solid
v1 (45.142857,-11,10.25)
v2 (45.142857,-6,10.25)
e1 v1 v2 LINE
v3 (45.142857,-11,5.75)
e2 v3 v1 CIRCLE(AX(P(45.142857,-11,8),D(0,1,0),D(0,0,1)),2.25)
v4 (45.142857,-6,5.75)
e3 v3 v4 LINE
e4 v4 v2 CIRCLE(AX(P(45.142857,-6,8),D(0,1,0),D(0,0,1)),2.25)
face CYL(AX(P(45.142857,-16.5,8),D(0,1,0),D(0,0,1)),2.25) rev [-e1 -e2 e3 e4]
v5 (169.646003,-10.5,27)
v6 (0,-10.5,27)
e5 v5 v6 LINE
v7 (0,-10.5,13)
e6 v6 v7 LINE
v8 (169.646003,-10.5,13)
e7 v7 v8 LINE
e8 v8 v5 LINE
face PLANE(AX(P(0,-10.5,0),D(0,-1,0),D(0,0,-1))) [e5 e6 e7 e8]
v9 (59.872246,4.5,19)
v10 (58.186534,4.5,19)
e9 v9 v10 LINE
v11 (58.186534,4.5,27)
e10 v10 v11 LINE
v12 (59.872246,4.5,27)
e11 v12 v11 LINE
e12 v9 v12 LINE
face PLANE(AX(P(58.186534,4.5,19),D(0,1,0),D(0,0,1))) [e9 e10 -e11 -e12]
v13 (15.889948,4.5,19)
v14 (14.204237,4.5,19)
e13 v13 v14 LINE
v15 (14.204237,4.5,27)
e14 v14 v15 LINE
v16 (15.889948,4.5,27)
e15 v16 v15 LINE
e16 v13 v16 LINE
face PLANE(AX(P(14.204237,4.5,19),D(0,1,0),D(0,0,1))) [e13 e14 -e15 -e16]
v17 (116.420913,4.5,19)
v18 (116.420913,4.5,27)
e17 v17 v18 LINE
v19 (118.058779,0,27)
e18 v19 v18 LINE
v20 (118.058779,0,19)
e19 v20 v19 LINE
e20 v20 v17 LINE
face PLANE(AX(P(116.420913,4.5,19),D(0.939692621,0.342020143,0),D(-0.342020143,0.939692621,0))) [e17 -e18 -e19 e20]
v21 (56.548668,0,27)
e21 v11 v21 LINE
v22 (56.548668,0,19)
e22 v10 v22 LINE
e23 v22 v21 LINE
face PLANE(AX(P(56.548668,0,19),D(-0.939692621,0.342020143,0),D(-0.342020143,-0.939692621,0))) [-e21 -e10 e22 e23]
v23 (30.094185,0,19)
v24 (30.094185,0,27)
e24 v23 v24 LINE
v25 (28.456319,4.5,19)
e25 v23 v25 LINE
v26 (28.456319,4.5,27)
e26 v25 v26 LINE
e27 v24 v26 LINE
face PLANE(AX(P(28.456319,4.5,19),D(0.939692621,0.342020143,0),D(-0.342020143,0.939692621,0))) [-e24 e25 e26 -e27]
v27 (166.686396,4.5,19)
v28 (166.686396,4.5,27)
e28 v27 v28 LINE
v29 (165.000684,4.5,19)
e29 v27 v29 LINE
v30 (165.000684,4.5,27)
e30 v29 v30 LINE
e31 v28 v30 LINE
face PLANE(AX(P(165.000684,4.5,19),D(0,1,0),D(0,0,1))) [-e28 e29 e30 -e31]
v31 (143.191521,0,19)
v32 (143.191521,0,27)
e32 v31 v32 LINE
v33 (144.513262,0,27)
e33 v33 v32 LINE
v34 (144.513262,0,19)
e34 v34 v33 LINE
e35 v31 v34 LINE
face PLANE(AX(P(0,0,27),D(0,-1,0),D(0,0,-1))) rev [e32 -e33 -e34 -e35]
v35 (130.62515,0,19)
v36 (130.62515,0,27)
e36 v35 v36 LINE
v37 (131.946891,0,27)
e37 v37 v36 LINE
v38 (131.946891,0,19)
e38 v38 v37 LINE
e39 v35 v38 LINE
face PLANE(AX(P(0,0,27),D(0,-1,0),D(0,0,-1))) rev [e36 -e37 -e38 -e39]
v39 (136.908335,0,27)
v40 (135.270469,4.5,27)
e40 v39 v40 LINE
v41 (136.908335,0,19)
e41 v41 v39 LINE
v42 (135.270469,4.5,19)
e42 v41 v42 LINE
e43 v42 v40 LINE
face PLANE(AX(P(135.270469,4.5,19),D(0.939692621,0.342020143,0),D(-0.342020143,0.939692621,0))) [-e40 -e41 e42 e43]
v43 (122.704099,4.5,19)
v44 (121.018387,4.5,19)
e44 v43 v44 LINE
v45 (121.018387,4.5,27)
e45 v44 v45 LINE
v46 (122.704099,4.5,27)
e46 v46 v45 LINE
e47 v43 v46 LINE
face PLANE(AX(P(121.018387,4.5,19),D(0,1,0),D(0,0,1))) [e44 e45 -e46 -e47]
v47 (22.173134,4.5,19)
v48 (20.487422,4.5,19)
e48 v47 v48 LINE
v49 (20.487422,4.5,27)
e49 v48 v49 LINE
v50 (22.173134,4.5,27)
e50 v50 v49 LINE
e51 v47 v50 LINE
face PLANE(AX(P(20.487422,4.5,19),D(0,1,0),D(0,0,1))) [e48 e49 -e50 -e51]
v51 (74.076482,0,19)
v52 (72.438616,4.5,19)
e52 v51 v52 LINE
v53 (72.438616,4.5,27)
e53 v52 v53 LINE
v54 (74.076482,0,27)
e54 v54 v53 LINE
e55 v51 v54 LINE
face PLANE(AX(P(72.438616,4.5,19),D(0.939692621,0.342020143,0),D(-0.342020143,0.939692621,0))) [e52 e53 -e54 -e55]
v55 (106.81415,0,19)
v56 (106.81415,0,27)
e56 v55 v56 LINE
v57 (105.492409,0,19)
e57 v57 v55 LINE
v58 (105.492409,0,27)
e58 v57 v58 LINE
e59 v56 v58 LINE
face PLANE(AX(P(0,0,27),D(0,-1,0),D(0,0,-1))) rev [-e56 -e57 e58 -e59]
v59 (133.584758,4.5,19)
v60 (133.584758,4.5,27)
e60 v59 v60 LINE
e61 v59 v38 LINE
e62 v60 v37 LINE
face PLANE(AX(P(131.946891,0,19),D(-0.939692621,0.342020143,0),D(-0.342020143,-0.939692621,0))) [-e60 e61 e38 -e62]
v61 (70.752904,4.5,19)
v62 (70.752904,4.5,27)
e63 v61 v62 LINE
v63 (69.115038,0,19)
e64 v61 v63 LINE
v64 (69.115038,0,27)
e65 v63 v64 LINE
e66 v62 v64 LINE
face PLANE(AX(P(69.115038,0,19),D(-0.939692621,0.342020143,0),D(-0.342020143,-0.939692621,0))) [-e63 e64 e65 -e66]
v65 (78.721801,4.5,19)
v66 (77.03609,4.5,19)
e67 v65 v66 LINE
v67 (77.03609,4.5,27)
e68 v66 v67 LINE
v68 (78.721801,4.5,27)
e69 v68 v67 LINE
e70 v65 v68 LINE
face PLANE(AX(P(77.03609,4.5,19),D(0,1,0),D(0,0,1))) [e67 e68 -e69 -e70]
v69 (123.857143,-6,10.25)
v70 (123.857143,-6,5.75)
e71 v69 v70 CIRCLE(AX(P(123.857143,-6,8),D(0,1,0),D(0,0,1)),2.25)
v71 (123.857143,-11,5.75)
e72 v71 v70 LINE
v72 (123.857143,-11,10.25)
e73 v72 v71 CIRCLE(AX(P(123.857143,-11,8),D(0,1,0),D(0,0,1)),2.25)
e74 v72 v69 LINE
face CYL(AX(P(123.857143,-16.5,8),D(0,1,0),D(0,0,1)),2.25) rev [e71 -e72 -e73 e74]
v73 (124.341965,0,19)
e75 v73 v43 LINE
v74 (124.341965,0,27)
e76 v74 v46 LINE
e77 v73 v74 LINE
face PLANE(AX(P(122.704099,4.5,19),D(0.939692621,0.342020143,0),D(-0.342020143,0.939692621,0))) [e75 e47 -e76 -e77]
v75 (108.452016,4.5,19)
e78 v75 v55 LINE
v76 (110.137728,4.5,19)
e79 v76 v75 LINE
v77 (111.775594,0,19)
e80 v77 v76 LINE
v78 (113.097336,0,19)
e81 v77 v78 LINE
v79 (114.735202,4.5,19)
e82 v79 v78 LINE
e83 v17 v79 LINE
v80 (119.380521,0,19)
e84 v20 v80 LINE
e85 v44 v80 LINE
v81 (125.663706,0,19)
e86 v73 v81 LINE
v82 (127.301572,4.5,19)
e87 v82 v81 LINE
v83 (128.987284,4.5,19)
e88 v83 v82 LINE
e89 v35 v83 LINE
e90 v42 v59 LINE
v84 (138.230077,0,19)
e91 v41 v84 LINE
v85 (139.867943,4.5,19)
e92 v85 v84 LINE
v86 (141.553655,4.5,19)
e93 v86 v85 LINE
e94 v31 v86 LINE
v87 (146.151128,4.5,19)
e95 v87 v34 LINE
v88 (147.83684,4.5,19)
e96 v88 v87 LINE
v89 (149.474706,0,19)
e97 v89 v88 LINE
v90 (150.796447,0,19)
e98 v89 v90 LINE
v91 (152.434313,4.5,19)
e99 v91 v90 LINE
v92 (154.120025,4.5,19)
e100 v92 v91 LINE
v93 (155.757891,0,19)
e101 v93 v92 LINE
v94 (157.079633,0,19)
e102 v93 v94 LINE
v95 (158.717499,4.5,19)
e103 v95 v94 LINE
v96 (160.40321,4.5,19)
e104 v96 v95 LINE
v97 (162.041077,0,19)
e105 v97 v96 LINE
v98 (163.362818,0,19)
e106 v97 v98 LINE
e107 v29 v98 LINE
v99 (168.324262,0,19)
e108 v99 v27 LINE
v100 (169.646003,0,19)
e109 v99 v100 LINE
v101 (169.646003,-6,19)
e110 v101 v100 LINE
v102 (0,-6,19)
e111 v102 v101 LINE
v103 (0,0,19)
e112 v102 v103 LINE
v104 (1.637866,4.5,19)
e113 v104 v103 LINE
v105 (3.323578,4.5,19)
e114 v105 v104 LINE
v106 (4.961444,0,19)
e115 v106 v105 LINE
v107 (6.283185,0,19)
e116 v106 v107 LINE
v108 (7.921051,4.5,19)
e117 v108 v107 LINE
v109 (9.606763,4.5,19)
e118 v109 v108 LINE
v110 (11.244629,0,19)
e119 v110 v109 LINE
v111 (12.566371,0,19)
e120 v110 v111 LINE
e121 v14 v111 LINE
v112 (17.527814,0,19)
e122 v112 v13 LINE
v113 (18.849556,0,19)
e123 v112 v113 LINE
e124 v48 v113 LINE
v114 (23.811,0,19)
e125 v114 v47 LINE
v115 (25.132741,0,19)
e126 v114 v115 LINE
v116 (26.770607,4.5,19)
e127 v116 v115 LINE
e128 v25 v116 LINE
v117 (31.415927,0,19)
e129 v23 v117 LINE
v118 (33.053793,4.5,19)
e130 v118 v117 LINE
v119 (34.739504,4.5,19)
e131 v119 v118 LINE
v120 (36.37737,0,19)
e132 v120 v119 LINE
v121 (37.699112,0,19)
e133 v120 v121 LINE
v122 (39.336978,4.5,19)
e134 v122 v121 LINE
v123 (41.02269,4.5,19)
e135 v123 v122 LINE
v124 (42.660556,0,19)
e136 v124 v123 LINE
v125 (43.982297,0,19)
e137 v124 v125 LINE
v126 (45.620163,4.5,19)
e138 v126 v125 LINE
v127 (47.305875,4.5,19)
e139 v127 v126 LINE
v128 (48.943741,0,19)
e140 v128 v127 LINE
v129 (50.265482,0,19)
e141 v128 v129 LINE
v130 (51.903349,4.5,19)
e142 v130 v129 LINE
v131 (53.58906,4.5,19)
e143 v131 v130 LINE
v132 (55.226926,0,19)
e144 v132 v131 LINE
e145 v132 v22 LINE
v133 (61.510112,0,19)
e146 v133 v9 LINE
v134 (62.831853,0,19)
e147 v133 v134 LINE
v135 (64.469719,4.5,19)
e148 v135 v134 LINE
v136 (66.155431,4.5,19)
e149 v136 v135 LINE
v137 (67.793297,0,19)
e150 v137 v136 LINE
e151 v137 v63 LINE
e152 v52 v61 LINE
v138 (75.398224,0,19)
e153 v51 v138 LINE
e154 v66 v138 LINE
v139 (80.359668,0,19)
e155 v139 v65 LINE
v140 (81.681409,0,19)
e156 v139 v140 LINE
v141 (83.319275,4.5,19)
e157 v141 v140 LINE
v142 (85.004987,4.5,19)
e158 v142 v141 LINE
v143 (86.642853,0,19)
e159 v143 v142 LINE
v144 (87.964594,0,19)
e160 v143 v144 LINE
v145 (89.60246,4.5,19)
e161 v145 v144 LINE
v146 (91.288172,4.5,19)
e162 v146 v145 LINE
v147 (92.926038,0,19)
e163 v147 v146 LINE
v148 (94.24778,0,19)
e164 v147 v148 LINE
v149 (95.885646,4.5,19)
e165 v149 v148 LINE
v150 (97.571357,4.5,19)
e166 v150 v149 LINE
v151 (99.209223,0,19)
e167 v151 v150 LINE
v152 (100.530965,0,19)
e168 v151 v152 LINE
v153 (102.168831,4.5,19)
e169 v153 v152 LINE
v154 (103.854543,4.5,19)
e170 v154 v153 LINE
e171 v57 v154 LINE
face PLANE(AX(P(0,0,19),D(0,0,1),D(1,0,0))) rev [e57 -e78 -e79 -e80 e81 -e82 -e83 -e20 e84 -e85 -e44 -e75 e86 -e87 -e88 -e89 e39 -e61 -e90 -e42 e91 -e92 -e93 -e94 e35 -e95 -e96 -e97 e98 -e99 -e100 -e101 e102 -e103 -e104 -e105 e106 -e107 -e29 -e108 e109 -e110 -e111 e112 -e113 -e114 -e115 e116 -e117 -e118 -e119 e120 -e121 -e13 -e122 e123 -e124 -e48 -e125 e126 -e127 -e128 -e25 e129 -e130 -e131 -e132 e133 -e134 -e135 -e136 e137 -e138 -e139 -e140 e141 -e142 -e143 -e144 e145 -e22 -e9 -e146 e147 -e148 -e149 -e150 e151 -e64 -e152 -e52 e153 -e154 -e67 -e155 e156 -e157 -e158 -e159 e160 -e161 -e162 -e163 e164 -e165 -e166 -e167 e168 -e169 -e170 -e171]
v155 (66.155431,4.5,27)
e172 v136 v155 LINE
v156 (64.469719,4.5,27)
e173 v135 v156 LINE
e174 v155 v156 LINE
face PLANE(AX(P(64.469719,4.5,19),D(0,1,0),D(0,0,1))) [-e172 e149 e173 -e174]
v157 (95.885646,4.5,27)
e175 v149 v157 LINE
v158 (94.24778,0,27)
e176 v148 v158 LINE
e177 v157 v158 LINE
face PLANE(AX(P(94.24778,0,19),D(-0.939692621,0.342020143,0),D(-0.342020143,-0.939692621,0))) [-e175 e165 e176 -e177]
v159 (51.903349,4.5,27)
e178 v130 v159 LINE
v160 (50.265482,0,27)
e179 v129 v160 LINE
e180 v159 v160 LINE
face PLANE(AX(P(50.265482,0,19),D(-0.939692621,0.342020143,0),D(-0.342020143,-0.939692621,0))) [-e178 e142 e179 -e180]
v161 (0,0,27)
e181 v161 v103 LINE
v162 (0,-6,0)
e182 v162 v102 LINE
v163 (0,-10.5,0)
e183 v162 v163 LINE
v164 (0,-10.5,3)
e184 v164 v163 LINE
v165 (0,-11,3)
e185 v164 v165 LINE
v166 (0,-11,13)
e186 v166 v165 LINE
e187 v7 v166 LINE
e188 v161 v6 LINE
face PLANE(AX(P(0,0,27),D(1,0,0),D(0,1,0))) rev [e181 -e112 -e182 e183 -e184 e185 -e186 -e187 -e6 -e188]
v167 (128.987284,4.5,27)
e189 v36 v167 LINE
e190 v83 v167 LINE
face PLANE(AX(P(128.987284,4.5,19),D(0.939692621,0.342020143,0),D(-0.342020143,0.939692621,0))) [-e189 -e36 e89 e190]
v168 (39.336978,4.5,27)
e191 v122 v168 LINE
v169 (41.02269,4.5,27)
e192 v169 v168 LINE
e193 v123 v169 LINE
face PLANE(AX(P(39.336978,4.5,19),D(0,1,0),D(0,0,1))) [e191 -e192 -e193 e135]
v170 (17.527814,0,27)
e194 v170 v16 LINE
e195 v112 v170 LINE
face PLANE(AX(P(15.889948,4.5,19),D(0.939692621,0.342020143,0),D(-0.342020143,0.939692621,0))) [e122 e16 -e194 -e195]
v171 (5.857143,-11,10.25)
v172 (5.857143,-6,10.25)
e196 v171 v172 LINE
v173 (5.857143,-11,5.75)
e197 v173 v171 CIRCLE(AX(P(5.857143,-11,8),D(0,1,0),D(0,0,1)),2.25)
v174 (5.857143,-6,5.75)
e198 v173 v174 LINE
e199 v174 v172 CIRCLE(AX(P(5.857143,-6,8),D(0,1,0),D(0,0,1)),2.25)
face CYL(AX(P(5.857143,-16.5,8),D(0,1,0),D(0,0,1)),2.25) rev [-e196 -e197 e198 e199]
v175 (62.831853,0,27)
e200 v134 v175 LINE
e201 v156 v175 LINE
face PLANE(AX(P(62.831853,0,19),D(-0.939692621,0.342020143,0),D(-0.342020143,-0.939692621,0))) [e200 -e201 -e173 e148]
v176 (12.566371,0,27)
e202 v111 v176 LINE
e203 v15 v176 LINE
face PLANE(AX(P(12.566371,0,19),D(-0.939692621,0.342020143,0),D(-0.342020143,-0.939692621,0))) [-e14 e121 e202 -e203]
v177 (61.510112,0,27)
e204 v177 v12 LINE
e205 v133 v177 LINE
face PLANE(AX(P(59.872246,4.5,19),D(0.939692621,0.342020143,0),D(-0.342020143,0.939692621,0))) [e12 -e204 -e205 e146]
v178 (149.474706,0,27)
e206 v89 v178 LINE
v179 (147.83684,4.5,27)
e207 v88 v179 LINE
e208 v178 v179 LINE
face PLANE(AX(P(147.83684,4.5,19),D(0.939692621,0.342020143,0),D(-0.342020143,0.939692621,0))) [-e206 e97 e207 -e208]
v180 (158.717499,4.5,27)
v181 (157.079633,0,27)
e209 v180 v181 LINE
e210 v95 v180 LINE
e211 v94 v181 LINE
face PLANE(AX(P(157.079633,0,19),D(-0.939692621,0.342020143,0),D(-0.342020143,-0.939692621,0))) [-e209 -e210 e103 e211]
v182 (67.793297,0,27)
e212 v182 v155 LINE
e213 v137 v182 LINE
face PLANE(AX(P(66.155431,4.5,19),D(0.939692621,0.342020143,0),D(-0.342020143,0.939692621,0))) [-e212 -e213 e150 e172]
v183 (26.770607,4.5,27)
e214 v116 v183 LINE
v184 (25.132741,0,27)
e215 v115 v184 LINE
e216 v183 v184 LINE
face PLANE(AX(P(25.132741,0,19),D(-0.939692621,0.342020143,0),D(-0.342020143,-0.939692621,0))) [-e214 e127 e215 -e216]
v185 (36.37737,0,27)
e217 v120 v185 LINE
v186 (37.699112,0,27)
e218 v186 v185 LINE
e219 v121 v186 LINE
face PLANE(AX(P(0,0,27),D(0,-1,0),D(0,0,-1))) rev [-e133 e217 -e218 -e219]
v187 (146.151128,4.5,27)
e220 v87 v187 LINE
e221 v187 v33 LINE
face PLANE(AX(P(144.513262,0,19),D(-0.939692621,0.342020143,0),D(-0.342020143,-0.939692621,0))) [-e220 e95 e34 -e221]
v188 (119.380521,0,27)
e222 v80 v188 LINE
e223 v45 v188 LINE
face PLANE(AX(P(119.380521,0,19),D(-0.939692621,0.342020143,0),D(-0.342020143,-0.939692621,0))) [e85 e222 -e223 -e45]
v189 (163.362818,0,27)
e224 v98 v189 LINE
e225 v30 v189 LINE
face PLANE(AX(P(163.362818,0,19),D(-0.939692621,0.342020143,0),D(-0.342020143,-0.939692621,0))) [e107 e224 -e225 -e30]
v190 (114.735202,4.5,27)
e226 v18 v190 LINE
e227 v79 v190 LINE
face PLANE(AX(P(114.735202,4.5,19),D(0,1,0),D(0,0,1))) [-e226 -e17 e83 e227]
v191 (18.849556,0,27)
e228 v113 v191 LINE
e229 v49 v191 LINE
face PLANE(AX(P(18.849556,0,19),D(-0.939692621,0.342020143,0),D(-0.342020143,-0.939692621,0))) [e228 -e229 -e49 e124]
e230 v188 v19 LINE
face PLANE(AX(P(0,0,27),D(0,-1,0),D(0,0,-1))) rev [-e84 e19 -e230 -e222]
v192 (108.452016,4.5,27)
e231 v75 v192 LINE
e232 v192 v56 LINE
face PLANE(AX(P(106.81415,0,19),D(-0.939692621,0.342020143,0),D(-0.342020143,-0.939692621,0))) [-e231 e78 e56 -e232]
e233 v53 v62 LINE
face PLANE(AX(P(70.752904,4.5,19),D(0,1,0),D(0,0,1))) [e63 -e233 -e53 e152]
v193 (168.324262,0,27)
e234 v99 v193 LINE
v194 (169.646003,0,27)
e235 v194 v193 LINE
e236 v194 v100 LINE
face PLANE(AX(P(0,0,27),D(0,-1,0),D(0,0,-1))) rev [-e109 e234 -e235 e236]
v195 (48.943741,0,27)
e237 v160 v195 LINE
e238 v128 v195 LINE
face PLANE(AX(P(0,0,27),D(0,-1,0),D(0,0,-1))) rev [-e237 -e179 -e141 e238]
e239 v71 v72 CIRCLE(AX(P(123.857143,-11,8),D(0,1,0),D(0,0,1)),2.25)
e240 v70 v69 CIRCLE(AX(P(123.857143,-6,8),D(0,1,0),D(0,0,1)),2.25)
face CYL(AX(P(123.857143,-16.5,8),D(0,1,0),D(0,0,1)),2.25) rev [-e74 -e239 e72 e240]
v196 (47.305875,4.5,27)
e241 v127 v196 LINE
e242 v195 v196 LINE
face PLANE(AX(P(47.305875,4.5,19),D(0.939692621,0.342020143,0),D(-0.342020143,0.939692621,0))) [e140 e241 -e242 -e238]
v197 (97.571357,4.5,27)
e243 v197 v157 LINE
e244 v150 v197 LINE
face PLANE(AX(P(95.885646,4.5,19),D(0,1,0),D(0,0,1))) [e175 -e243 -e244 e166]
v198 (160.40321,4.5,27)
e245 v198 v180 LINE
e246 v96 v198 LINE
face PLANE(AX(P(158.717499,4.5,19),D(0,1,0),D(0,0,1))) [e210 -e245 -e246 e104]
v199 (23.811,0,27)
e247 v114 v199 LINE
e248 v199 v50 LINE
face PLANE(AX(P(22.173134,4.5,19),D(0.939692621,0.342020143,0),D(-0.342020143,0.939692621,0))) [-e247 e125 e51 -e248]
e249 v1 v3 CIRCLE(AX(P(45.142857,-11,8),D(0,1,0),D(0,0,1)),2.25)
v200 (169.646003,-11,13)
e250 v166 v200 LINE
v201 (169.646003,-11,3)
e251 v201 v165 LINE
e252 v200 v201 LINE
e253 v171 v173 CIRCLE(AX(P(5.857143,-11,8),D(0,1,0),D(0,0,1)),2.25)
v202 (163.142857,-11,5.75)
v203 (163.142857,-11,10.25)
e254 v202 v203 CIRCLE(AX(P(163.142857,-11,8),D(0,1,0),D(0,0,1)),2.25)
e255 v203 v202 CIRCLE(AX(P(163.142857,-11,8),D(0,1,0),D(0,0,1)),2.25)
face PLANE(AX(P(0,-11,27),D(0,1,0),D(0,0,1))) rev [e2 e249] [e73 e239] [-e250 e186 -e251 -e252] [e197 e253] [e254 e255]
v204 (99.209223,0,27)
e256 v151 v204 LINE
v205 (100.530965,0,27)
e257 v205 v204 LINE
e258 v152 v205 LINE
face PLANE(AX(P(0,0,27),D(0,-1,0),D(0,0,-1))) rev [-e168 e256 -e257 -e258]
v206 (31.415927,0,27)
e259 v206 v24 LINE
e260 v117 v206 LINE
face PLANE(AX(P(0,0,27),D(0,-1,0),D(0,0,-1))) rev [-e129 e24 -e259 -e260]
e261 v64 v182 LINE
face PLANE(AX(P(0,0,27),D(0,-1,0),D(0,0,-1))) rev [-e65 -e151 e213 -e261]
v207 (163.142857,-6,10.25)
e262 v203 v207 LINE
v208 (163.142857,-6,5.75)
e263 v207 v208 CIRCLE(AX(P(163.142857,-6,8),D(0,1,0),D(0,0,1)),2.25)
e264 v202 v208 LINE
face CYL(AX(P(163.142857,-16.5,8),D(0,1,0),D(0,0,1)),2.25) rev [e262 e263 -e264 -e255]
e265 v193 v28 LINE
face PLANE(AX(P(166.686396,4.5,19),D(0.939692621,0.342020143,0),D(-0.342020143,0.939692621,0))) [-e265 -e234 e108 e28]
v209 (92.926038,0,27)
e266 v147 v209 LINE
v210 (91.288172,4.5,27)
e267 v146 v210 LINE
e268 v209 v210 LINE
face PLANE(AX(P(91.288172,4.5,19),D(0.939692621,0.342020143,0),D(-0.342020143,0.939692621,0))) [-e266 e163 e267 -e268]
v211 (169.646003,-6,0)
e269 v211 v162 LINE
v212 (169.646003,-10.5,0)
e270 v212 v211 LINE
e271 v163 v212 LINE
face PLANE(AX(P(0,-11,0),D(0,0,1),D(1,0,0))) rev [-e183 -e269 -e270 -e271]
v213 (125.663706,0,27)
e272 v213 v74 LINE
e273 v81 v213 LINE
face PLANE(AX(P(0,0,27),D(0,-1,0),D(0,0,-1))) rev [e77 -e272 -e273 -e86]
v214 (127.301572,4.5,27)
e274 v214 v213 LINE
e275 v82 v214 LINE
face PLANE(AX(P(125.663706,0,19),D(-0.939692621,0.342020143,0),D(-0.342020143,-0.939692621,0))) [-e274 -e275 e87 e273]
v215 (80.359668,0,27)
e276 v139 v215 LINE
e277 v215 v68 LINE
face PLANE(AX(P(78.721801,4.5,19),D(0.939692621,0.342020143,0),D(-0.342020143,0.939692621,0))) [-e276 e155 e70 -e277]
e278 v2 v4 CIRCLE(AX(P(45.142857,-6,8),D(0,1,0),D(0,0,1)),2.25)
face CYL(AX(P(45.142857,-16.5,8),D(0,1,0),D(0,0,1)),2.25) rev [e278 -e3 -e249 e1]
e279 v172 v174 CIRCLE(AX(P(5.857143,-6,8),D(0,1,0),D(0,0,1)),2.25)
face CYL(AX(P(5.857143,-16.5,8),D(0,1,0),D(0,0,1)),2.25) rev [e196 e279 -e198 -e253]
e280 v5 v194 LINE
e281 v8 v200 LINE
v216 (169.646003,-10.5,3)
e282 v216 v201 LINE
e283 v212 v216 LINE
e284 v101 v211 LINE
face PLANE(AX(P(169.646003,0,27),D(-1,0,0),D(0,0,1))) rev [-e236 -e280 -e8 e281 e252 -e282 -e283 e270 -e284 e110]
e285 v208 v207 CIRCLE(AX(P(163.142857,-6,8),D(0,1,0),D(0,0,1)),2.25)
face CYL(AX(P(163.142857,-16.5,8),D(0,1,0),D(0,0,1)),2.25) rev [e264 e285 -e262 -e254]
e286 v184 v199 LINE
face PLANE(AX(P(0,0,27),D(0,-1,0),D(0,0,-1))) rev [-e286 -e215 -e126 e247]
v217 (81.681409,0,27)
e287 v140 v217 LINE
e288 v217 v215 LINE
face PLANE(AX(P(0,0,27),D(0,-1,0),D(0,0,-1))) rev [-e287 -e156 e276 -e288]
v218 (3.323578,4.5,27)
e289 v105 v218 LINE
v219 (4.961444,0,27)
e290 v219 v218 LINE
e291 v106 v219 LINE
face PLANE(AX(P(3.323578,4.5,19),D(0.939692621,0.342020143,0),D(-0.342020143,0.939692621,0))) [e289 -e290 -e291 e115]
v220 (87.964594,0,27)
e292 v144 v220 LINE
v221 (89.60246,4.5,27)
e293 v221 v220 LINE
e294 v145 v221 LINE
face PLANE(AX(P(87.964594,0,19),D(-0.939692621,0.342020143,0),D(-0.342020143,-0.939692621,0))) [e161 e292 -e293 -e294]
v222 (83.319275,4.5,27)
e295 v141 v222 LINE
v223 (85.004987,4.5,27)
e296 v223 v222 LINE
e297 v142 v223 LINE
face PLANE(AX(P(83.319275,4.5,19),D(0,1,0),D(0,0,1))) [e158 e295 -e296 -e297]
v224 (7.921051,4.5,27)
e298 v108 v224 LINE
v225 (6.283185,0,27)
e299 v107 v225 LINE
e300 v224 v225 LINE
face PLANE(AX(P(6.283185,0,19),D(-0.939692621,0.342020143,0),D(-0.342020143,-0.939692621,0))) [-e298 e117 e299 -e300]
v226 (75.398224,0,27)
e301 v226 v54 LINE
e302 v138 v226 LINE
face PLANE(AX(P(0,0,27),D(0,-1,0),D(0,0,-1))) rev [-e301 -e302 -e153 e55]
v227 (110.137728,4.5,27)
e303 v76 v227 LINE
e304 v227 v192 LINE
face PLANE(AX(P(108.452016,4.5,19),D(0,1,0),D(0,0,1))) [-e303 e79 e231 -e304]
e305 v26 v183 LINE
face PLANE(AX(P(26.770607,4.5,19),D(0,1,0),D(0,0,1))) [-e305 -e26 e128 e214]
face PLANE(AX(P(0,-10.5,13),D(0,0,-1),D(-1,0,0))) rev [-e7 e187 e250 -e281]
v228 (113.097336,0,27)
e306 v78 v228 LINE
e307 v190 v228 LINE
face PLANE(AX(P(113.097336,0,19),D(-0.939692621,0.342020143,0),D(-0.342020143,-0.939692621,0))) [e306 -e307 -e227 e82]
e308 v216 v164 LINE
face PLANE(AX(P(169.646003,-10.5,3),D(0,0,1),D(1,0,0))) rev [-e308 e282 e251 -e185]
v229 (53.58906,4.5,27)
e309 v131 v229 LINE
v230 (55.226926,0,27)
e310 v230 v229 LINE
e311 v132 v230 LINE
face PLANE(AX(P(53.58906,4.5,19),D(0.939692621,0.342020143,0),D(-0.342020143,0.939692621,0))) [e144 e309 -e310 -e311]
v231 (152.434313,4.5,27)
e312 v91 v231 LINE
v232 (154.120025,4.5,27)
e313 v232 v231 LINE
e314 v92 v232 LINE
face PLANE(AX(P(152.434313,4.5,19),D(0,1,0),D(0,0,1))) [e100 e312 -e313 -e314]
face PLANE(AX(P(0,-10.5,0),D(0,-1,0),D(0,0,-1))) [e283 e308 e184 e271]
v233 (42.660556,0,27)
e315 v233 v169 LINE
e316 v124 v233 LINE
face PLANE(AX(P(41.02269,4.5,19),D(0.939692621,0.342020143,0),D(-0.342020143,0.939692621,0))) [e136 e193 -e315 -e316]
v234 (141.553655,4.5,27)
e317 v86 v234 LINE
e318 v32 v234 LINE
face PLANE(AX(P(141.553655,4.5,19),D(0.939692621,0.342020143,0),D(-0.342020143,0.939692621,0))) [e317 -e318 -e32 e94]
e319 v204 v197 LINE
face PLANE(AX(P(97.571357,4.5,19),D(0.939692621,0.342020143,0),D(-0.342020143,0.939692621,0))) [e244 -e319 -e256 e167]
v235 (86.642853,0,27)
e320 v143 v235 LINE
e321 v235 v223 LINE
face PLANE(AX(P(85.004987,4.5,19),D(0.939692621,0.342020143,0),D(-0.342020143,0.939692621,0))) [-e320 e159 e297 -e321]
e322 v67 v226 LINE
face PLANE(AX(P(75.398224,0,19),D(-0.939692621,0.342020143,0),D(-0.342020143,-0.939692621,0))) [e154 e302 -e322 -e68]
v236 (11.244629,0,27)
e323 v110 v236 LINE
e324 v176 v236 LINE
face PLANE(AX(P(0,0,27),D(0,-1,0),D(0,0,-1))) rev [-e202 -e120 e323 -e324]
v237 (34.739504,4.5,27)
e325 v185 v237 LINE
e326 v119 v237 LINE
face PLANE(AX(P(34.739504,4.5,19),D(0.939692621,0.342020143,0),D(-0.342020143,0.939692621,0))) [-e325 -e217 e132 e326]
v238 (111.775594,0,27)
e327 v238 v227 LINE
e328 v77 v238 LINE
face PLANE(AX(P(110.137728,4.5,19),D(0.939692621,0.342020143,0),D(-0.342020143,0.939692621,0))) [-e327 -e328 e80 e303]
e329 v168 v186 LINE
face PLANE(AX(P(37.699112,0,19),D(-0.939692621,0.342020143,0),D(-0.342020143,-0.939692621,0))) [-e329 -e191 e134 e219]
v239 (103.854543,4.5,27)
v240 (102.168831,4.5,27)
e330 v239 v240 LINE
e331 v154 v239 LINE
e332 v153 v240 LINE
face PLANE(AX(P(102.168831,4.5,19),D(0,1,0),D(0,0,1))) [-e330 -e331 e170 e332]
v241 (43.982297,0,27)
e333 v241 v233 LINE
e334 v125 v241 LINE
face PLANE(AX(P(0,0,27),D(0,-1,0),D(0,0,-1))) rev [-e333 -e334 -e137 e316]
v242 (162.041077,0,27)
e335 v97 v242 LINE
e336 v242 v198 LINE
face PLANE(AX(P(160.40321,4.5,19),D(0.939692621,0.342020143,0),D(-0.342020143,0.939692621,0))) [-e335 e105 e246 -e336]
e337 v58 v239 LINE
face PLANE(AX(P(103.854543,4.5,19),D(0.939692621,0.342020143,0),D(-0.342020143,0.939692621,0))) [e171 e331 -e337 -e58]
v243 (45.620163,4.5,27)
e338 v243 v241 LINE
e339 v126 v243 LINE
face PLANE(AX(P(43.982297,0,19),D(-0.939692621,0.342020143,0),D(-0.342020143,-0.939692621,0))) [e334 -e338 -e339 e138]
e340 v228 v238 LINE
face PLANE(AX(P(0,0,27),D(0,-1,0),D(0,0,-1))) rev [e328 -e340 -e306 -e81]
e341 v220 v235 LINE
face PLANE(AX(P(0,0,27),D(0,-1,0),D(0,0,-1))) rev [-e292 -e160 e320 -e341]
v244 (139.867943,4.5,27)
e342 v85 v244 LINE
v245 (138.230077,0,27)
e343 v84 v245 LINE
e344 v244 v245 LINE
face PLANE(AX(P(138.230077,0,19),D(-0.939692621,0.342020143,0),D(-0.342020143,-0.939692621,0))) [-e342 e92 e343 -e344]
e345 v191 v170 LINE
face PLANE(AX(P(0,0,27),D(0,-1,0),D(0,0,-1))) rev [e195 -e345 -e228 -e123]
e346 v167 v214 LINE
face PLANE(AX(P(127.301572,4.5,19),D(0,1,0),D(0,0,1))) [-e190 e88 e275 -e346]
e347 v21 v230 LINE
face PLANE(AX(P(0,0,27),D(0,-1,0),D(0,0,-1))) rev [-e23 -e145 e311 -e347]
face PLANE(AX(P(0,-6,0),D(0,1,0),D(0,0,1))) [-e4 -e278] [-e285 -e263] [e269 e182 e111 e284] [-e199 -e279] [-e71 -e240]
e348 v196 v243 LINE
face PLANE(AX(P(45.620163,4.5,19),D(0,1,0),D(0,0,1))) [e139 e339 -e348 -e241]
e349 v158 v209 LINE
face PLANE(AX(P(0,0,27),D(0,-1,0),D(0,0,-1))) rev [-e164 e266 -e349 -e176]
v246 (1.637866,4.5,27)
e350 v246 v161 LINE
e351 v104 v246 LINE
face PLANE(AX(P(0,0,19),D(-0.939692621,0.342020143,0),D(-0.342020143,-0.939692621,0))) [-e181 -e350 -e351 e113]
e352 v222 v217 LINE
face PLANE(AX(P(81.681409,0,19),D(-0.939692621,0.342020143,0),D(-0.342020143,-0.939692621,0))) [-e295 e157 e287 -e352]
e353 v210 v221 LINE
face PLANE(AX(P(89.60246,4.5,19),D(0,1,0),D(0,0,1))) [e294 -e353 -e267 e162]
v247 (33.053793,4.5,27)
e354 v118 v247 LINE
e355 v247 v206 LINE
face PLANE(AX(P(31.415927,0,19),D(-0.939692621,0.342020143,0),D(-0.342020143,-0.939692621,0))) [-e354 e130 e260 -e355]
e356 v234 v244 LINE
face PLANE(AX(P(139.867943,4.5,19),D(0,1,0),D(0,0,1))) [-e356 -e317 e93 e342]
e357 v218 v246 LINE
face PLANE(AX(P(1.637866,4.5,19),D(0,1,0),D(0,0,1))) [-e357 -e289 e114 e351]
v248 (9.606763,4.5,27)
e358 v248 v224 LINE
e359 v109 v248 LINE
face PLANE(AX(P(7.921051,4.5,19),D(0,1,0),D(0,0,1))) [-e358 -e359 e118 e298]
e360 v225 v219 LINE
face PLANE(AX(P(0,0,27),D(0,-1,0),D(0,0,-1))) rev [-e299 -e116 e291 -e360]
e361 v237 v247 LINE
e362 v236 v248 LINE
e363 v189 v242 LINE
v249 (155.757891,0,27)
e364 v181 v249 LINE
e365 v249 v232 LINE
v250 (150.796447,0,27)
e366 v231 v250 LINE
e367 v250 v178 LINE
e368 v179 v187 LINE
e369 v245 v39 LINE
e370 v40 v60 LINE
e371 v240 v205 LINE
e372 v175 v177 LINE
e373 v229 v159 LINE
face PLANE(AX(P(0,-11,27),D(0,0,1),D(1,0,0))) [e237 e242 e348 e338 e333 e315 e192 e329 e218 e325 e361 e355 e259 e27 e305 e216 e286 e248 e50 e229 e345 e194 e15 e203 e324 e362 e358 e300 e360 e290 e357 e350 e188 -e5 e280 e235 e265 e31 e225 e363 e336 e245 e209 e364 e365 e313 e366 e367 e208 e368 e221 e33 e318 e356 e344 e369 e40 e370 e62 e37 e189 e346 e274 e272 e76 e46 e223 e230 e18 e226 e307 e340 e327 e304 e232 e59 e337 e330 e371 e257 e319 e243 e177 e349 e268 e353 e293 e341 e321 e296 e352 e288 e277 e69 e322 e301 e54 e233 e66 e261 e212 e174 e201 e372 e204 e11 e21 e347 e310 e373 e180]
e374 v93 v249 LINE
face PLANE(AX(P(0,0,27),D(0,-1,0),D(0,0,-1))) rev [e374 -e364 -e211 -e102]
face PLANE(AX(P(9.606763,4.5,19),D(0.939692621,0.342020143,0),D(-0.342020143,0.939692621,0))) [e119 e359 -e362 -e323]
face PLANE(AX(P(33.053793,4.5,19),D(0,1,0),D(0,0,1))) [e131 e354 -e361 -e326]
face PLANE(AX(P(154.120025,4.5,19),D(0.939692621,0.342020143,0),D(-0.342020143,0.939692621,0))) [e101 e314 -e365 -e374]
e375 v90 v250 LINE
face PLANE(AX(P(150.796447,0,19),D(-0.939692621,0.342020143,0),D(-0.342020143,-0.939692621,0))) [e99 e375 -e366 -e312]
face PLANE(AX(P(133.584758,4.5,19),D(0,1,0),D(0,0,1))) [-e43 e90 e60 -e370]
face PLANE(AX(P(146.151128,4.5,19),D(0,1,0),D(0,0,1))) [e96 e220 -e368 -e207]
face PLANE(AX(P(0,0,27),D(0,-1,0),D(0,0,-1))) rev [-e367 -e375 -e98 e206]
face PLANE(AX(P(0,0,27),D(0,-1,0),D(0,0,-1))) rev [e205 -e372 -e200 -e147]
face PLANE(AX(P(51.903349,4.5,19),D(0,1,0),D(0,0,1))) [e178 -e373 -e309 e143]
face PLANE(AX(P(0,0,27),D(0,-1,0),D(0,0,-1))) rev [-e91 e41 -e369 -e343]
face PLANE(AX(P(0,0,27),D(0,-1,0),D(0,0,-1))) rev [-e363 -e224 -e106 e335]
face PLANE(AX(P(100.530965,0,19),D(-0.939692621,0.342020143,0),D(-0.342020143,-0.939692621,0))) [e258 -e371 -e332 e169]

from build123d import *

# Parameters (mm, degrees)
SKETCH1_W              = 169.646003294
SKETCH1_H              = 11
EXTRUDE1_DEPTH         = 27
EXTRUDE2_DEPTH         = 8
LPATTERN1_COUNT        = 27
LPATTERN1_PITCH        = 6.283185307
SKETCH_1_W             = 169.646003294
SKETCH_1_H             = 19
CUT_EXTRUDE_1_DEPTH    = 6
SKETCH_3_R             = 2.25
CUT_EXTRUDE_2_DEPTH    = 10.5
PATTERN_LINEAR_2_COUNT = 2
PATTERN_LINEAR_2_PITCH = 118
SKETCH_5_W             = 169.646003294
SKETCH_5_H             = 14
SKETCH_5_H_2           = 3
CUT_EXTRUDE_3_DEPTH    = 0.5


with BuildPart() as part:
    # Sketch1 → Extrude1 (new body)
    with BuildSketch(Plane.XY):
        with Locations((84.823001647, -5.5)):
            Rectangle(SKETCH1_W, SKETCH1_H)
    extrude(amount=EXTRUDE1_DEPTH)

    # Sketch2 → Extrude2 (add)
    with BuildSketch(Plane.XY.offset(27)):
        Polygon((0, 0), (1.637866054, 4.5), (3.323577771, 4.5), (4.961443825, 0), align=None)
    extrude2 = extrude(amount=-EXTRUDE2_DEPTH)

    # LPattern1: Extrude2 ×27
    with Locations(*[(i * LPATTERN1_PITCH, 0, 0) for i in range(1, LPATTERN1_COUNT)]):
        add(extrude2)

    # 草图1 → 切除-拉伸1 (cut)
    with BuildSketch(Plane(origin=(0, 0, 0), x_dir=(1, 0, 0), z_dir=(0, 1, 0))):
        with Locations((84.823001647, -9.5)):
            Rectangle(SKETCH_1_W, SKETCH_1_H)
    extrude(amount=-CUT_EXTRUDE_1_DEPTH, mode=Mode.SUBTRACT)

    # 草图3 → 切除-拉伸2 (cut)
    with BuildSketch(Plane(origin=(0, -6, 0), x_dir=(1, 0, 0), z_dir=(0, 1, 0))):
        with Locations(Location((5.857142857, -8, 0), (0, 0, 270))):
            Circle(SKETCH_3_R)
        with Locations(Location((45.142857143, -8, 0), (0, 0, 270))):
            Circle(SKETCH_3_R)
    cut_extrude_2 = extrude(amount=-CUT_EXTRUDE_2_DEPTH, mode=Mode.SUBTRACT)

    # 阵列(线性)2: 切除-拉伸2 ×2
    with Locations(*[(i * PATTERN_LINEAR_2_PITCH, 0, 0) for i in range(1, PATTERN_LINEAR_2_COUNT)]):
        add(cut_extrude_2, mode=Mode.SUBTRACT)

    # 草图5 → 切除-拉伸3 (cut)
    with BuildSketch(Plane.XZ.offset(11)):
        with Locations((84.823001647, 20)):
            Rectangle(SKETCH_5_W, SKETCH_5_H)
        with Locations((84.823001647, 1.5)):
            Rectangle(SKETCH_5_W, SKETCH_5_H_2)
    extrude(amount=-CUT_EXTRUDE_3_DEPTH, mode=Mode.SUBTRACT)


solid = part.part
